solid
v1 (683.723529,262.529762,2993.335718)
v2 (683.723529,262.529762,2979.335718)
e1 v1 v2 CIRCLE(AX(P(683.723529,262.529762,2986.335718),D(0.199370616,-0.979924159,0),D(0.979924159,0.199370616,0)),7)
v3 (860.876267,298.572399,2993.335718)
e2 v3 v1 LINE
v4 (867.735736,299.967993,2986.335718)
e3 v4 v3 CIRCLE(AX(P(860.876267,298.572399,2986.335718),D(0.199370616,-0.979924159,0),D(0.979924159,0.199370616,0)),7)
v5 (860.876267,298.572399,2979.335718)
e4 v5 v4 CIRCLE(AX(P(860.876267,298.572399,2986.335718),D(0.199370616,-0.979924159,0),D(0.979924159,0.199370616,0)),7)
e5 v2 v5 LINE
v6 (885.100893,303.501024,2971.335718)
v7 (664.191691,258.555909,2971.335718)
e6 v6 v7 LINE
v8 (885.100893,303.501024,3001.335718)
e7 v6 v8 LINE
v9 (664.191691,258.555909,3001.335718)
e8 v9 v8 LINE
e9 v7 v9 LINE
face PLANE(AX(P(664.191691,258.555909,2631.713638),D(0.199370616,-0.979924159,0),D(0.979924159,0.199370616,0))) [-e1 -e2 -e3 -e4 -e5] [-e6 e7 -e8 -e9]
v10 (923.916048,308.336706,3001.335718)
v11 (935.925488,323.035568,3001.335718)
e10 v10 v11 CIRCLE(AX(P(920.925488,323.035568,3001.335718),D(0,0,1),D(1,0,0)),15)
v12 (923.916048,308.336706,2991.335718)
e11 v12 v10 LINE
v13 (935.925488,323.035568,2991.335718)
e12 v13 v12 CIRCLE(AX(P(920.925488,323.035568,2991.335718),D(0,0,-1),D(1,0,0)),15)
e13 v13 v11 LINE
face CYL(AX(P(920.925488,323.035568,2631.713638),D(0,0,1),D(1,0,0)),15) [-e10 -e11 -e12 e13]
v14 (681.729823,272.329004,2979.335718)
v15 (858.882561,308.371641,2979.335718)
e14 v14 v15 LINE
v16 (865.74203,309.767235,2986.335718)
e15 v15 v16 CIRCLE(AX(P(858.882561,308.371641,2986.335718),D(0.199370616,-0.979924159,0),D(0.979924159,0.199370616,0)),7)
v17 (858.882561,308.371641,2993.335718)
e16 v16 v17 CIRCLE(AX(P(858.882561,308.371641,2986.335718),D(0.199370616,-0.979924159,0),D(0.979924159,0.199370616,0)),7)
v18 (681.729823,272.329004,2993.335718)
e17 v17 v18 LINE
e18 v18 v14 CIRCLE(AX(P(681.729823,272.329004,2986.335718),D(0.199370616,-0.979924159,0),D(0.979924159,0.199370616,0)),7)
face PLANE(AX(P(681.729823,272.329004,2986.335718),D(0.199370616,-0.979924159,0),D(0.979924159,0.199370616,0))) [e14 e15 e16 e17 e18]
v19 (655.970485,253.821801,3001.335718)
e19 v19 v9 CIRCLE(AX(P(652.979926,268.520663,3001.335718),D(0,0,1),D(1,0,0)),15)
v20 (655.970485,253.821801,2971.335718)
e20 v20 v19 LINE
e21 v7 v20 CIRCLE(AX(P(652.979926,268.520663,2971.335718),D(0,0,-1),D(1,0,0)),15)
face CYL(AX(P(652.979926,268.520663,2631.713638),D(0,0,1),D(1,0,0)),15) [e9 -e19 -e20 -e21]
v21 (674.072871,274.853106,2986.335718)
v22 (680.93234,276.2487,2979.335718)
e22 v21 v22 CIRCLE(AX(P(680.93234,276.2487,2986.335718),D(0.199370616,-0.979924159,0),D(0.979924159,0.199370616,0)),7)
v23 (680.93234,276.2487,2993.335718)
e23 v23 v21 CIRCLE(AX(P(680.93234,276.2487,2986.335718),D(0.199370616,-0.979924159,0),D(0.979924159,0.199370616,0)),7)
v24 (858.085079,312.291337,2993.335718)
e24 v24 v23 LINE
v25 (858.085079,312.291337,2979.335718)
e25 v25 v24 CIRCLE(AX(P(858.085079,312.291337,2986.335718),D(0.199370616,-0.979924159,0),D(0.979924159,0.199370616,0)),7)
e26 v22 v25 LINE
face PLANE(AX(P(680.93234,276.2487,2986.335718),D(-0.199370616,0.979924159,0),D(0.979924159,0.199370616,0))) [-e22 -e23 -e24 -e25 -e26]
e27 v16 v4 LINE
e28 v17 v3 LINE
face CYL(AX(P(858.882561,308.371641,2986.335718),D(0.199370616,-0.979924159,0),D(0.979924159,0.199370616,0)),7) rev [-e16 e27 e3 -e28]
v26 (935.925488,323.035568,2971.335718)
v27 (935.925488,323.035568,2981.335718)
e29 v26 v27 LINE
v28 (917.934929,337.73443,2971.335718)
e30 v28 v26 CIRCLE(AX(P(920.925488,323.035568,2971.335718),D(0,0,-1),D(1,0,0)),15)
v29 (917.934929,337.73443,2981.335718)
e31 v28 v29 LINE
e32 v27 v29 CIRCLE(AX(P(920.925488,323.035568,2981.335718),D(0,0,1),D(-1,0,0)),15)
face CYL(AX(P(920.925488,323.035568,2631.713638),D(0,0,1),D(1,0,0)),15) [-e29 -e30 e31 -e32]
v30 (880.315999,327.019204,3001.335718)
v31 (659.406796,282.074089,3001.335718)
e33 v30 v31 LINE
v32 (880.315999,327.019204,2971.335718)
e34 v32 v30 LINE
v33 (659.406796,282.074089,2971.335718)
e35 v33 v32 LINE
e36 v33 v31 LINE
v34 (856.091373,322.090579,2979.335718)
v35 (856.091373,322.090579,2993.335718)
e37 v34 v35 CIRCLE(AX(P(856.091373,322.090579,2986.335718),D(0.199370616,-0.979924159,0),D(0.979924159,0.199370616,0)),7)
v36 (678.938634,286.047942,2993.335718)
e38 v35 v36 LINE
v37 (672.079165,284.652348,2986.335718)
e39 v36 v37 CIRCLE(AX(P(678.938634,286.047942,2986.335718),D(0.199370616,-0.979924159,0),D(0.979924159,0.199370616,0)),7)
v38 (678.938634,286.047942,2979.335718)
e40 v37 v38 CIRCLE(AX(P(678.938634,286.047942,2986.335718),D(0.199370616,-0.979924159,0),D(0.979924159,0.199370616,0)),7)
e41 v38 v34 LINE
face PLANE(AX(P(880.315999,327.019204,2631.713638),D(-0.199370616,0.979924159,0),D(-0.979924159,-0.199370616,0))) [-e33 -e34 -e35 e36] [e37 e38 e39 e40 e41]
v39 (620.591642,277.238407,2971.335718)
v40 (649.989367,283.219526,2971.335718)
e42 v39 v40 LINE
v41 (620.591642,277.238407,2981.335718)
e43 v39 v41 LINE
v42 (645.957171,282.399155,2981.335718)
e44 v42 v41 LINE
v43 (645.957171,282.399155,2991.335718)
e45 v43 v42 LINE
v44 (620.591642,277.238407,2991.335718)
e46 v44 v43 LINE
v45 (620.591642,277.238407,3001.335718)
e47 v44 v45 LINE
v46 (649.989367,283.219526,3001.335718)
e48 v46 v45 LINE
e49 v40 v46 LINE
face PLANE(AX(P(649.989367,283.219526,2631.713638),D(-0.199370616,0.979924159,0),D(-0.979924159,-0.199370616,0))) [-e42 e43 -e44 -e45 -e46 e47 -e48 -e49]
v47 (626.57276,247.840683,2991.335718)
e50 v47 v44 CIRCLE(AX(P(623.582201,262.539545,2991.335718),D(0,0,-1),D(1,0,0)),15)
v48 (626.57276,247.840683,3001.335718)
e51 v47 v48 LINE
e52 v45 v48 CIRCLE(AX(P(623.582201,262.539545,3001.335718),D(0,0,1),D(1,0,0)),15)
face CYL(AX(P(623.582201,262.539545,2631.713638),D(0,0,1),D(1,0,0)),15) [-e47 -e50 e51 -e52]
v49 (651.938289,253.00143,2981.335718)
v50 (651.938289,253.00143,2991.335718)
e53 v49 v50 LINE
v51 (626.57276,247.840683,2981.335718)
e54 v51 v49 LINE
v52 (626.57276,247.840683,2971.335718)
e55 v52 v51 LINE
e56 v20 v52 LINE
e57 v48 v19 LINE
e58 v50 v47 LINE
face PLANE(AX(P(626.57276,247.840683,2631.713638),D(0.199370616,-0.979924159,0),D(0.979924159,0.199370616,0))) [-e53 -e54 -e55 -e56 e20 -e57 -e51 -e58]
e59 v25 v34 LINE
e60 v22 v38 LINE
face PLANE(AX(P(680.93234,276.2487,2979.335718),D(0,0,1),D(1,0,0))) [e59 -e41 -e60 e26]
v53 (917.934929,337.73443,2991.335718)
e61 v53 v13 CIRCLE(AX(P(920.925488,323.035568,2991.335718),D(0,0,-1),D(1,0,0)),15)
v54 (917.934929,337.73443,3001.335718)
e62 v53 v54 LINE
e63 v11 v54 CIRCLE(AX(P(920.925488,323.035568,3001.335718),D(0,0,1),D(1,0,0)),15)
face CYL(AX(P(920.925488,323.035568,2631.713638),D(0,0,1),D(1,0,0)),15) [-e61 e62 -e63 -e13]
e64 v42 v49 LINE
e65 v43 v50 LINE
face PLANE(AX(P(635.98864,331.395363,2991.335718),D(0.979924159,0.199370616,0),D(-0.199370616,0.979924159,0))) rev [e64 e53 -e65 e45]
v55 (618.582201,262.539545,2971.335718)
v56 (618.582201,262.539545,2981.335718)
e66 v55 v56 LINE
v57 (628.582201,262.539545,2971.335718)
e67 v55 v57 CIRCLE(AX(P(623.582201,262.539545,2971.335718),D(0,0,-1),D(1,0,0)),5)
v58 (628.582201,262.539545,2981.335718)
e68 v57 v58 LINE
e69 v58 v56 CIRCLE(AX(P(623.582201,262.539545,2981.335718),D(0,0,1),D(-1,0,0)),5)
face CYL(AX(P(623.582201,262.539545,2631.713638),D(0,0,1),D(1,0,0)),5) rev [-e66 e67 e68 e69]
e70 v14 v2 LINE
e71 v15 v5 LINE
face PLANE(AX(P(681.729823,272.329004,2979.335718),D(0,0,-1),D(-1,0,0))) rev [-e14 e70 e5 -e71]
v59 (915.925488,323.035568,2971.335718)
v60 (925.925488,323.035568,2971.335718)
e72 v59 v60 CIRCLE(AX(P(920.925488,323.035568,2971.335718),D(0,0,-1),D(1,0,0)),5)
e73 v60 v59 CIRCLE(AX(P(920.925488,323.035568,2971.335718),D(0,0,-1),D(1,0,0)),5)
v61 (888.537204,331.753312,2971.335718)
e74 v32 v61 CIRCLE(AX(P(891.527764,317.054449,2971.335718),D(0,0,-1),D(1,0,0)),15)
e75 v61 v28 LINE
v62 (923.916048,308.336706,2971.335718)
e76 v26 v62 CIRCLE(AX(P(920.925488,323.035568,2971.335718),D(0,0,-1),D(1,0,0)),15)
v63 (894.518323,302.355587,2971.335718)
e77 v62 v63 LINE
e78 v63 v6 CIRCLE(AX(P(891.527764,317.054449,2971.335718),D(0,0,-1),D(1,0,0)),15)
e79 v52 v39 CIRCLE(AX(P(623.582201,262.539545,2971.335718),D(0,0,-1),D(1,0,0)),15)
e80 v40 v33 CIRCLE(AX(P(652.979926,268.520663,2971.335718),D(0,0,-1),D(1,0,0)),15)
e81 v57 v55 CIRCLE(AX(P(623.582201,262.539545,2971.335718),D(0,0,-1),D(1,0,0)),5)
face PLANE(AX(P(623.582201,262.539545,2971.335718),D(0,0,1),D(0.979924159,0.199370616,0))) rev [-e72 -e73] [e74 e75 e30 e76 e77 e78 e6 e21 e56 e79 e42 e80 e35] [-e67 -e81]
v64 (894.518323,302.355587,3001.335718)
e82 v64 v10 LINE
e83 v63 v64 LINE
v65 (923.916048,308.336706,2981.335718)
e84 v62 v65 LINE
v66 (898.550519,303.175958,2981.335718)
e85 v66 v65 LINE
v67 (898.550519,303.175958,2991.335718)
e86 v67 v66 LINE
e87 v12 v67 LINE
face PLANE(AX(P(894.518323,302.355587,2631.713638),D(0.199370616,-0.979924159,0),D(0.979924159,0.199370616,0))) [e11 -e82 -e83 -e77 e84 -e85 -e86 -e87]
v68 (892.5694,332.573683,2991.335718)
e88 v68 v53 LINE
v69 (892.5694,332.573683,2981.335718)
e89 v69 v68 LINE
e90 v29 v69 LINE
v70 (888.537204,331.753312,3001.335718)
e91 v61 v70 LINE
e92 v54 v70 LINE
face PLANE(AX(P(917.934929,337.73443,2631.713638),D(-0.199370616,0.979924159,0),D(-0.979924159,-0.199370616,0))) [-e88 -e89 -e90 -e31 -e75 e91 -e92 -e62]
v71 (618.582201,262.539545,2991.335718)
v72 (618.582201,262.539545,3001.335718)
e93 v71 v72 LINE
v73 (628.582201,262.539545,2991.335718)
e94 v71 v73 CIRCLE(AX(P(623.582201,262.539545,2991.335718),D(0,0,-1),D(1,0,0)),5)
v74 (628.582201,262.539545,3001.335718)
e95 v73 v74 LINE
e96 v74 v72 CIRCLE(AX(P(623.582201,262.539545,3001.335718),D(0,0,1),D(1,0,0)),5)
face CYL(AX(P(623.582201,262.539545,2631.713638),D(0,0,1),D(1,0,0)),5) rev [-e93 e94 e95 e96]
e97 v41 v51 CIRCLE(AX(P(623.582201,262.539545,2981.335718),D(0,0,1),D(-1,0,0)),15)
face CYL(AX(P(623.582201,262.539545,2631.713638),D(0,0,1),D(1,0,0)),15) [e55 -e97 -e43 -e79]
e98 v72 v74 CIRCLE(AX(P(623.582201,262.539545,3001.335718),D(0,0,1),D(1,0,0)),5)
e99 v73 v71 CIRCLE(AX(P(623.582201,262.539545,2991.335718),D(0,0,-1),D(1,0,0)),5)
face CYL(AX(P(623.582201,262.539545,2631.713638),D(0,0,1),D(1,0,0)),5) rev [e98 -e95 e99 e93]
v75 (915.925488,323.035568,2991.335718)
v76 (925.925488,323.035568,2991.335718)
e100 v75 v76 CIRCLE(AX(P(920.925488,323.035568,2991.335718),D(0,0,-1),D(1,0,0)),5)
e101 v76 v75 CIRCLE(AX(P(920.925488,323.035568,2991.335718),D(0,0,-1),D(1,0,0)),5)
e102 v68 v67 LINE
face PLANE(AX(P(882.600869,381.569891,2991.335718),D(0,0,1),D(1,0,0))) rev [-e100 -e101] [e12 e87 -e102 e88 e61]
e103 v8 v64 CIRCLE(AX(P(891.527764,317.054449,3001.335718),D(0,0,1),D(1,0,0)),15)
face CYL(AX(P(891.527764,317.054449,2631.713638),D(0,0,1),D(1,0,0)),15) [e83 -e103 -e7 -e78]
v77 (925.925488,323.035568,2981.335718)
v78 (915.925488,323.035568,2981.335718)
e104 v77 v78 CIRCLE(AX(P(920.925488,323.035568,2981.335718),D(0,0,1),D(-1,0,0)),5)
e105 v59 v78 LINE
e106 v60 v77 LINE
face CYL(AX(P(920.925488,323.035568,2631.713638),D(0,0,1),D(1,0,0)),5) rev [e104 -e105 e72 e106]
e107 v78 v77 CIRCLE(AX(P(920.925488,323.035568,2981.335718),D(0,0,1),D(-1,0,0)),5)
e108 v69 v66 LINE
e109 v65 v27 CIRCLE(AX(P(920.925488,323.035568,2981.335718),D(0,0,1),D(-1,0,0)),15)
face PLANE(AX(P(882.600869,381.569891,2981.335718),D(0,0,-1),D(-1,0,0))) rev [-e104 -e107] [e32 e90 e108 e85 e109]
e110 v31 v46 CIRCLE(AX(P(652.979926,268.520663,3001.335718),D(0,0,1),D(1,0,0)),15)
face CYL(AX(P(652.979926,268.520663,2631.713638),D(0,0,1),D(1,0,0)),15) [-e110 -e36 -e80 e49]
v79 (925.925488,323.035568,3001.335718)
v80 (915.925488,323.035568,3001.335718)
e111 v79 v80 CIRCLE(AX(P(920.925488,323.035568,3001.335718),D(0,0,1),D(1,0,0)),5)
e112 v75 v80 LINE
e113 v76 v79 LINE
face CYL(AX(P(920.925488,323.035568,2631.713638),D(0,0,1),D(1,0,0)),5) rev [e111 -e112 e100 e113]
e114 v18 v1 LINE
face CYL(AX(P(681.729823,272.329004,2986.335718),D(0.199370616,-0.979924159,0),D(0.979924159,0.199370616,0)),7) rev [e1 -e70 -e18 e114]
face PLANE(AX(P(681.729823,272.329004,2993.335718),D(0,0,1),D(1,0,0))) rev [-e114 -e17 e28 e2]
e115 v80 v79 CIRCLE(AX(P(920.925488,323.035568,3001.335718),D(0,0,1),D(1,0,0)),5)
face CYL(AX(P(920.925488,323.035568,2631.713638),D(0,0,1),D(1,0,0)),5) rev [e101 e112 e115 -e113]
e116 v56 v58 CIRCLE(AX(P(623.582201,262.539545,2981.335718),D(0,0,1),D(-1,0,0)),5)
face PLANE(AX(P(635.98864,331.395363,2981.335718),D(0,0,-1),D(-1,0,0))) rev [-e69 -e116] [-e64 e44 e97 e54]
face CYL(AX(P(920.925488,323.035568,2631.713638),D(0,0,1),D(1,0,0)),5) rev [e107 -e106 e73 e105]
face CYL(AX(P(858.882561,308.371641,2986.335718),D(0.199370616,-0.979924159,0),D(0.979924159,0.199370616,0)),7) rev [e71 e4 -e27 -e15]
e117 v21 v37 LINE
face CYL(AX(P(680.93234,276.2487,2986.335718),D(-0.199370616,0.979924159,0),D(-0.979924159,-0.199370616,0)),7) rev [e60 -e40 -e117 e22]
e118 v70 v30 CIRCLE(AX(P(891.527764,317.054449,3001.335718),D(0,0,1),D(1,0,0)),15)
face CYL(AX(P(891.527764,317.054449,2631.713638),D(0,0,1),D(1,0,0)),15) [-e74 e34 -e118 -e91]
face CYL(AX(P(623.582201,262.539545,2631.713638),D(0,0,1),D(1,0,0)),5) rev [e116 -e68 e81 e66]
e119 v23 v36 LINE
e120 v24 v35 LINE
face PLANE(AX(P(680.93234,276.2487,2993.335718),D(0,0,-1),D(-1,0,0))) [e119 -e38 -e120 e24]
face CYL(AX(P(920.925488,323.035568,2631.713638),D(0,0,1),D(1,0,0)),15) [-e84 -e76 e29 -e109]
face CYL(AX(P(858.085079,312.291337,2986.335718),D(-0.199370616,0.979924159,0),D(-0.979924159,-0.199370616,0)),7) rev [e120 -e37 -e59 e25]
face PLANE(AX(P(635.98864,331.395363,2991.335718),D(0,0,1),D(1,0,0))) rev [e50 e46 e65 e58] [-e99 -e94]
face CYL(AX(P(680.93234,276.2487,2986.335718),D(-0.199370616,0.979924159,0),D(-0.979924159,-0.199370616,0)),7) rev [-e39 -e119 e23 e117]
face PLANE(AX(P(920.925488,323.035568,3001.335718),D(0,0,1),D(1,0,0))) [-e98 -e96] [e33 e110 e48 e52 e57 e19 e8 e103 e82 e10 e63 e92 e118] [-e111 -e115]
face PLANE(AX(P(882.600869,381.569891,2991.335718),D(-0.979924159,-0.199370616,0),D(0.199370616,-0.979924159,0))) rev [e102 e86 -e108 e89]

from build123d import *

# Parameters (mm, degrees)
BOSS_EXTRUDE1_DEPTH = 30
SKETCH2_W           = 45.814700403
SKETCH2_H           = 10
CUT_EXTRUDE1_DEPTH  = 80
CUT_EXTRUDE2_DEPTH  = 10


with BuildPart() as part:
    # Sketch1 → Boss-Extrude1 (new body)
    with BuildSketch(Plane.XY.offset(3001.335718486)):
        with BuildLine():
            Line((917.934929034, 337.734430273), (888.537204265, 331.753311783))
            ThreePointArc((888.537204265, 331.753311783), (884.042481487, 330.053316774), (880.315998683, 327.019203759))
            Line((880.315998683, 327.019203759), (659.406795905, 282.074088861))
            ThreePointArc((659.406795905, 282.074088861), (654.791020678, 283.41092652), (649.989366626, 283.21952579))
            Line((649.989366626, 283.21952579), (620.591641856, 277.2384073))
            ThreePointArc((620.591641856, 277.2384073), (608.883338717, 259.54898567), (626.572760347, 247.840682531))
            Line((626.572760347, 247.840682531), (655.970485116, 253.821801021))
            ThreePointArc((655.970485116, 253.821801021), (660.465207894, 255.521796031), (664.191690698, 258.555909045))
            Line((664.191690698, 258.555909045), (885.100893475, 303.501023943))
            ThreePointArc((885.100893475, 303.501023943), (889.716668703, 302.164186284), (894.518322755, 302.355587014))
            Line((894.518322755, 302.355587014), (923.916047524, 308.336705504))
            ThreePointArc((923.916047524, 308.336705504), (935.624350664, 326.026127134), (917.934929034, 337.734430273))
        make_face()
        with BuildLine():
            ThreePointArc((618.682580307, 261.542691833), (624.579054184, 257.63992412), (628.481821897, 263.536397997))
            ThreePointArc((628.481821897, 263.536397997), (622.58534802, 267.43916571), (618.682580307, 261.542691833))
        make_face(mode=Mode.SUBTRACT)
        with BuildLine():
            ThreePointArc((916.025867484, 322.038714807), (921.922341361, 318.135947094), (925.825109074, 324.032420971))
            ThreePointArc((925.825109074, 324.032420971), (919.928635197, 327.935188684), (916.025867484, 322.038714807))
        make_face(mode=Mode.SUBTRACT)
    extrude(amount=-BOSS_EXTRUDE1_DEPTH)

    # Sketch2 → Cut-Extrude1 (cut)
    with BuildSketch(Plane(origin=(-23.514742418, 115.577032406, 0), x_dir=(0.9799241589705207, 0.19937061635536468, 0), z_dir=(0.19937061635536468, -0.9799241589705207, 0))):
        with Locations((963.863089214, 2986.335718486)):
            Rectangle(SKETCH2_W, SKETCH2_H)
        with Locations((666.383780489, 2986.335718486)):
            Rectangle(SKETCH2_W, SKETCH2_H)
    extrude(amount=-CUT_EXTRUDE1_DEPTH, mode=Mode.SUBTRACT)

    # Sketch3 → Cut-Extrude2 (cut)
    with BuildSketch(Plane(origin=(-24.112854267, 118.516804882, 0), x_dir=(0.9799241589705208, 0.19937061635536377, 0), z_dir=(0.19937061635536377, -0.9799241589705208, 0))):
        with BuildLine():
            Line((722.337924675, 2993.335718486), (903.120015469, 2993.335718486))
            ThreePointArc((903.120015469, 2993.335718486), (910.120015469, 2986.335718486), (903.120015469, 2979.335718486))
            Line((903.120015469, 2979.335718486), (722.337924675, 2979.335718486))
            ThreePointArc((722.337924675, 2979.335718486), (715.337924675, 2986.335718486), (722.337924675, 2993.335718486))
        make_face()
    cut_extrude2 = extrude(amount=-CUT_EXTRUDE2_DEPTH, mode=Mode.SUBTRACT)

    # Mirror1: Cut-Extrude2 across plane
    add(cut_extrude2.mirror(Plane(origin=(-26.505301663, 130.27589479, 0), x_dir=(0, 0, 1), z_dir=(0.1993706163553639, -0.9799241589705208, 0))), mode=Mode.SUBTRACT)


solid = part.part
